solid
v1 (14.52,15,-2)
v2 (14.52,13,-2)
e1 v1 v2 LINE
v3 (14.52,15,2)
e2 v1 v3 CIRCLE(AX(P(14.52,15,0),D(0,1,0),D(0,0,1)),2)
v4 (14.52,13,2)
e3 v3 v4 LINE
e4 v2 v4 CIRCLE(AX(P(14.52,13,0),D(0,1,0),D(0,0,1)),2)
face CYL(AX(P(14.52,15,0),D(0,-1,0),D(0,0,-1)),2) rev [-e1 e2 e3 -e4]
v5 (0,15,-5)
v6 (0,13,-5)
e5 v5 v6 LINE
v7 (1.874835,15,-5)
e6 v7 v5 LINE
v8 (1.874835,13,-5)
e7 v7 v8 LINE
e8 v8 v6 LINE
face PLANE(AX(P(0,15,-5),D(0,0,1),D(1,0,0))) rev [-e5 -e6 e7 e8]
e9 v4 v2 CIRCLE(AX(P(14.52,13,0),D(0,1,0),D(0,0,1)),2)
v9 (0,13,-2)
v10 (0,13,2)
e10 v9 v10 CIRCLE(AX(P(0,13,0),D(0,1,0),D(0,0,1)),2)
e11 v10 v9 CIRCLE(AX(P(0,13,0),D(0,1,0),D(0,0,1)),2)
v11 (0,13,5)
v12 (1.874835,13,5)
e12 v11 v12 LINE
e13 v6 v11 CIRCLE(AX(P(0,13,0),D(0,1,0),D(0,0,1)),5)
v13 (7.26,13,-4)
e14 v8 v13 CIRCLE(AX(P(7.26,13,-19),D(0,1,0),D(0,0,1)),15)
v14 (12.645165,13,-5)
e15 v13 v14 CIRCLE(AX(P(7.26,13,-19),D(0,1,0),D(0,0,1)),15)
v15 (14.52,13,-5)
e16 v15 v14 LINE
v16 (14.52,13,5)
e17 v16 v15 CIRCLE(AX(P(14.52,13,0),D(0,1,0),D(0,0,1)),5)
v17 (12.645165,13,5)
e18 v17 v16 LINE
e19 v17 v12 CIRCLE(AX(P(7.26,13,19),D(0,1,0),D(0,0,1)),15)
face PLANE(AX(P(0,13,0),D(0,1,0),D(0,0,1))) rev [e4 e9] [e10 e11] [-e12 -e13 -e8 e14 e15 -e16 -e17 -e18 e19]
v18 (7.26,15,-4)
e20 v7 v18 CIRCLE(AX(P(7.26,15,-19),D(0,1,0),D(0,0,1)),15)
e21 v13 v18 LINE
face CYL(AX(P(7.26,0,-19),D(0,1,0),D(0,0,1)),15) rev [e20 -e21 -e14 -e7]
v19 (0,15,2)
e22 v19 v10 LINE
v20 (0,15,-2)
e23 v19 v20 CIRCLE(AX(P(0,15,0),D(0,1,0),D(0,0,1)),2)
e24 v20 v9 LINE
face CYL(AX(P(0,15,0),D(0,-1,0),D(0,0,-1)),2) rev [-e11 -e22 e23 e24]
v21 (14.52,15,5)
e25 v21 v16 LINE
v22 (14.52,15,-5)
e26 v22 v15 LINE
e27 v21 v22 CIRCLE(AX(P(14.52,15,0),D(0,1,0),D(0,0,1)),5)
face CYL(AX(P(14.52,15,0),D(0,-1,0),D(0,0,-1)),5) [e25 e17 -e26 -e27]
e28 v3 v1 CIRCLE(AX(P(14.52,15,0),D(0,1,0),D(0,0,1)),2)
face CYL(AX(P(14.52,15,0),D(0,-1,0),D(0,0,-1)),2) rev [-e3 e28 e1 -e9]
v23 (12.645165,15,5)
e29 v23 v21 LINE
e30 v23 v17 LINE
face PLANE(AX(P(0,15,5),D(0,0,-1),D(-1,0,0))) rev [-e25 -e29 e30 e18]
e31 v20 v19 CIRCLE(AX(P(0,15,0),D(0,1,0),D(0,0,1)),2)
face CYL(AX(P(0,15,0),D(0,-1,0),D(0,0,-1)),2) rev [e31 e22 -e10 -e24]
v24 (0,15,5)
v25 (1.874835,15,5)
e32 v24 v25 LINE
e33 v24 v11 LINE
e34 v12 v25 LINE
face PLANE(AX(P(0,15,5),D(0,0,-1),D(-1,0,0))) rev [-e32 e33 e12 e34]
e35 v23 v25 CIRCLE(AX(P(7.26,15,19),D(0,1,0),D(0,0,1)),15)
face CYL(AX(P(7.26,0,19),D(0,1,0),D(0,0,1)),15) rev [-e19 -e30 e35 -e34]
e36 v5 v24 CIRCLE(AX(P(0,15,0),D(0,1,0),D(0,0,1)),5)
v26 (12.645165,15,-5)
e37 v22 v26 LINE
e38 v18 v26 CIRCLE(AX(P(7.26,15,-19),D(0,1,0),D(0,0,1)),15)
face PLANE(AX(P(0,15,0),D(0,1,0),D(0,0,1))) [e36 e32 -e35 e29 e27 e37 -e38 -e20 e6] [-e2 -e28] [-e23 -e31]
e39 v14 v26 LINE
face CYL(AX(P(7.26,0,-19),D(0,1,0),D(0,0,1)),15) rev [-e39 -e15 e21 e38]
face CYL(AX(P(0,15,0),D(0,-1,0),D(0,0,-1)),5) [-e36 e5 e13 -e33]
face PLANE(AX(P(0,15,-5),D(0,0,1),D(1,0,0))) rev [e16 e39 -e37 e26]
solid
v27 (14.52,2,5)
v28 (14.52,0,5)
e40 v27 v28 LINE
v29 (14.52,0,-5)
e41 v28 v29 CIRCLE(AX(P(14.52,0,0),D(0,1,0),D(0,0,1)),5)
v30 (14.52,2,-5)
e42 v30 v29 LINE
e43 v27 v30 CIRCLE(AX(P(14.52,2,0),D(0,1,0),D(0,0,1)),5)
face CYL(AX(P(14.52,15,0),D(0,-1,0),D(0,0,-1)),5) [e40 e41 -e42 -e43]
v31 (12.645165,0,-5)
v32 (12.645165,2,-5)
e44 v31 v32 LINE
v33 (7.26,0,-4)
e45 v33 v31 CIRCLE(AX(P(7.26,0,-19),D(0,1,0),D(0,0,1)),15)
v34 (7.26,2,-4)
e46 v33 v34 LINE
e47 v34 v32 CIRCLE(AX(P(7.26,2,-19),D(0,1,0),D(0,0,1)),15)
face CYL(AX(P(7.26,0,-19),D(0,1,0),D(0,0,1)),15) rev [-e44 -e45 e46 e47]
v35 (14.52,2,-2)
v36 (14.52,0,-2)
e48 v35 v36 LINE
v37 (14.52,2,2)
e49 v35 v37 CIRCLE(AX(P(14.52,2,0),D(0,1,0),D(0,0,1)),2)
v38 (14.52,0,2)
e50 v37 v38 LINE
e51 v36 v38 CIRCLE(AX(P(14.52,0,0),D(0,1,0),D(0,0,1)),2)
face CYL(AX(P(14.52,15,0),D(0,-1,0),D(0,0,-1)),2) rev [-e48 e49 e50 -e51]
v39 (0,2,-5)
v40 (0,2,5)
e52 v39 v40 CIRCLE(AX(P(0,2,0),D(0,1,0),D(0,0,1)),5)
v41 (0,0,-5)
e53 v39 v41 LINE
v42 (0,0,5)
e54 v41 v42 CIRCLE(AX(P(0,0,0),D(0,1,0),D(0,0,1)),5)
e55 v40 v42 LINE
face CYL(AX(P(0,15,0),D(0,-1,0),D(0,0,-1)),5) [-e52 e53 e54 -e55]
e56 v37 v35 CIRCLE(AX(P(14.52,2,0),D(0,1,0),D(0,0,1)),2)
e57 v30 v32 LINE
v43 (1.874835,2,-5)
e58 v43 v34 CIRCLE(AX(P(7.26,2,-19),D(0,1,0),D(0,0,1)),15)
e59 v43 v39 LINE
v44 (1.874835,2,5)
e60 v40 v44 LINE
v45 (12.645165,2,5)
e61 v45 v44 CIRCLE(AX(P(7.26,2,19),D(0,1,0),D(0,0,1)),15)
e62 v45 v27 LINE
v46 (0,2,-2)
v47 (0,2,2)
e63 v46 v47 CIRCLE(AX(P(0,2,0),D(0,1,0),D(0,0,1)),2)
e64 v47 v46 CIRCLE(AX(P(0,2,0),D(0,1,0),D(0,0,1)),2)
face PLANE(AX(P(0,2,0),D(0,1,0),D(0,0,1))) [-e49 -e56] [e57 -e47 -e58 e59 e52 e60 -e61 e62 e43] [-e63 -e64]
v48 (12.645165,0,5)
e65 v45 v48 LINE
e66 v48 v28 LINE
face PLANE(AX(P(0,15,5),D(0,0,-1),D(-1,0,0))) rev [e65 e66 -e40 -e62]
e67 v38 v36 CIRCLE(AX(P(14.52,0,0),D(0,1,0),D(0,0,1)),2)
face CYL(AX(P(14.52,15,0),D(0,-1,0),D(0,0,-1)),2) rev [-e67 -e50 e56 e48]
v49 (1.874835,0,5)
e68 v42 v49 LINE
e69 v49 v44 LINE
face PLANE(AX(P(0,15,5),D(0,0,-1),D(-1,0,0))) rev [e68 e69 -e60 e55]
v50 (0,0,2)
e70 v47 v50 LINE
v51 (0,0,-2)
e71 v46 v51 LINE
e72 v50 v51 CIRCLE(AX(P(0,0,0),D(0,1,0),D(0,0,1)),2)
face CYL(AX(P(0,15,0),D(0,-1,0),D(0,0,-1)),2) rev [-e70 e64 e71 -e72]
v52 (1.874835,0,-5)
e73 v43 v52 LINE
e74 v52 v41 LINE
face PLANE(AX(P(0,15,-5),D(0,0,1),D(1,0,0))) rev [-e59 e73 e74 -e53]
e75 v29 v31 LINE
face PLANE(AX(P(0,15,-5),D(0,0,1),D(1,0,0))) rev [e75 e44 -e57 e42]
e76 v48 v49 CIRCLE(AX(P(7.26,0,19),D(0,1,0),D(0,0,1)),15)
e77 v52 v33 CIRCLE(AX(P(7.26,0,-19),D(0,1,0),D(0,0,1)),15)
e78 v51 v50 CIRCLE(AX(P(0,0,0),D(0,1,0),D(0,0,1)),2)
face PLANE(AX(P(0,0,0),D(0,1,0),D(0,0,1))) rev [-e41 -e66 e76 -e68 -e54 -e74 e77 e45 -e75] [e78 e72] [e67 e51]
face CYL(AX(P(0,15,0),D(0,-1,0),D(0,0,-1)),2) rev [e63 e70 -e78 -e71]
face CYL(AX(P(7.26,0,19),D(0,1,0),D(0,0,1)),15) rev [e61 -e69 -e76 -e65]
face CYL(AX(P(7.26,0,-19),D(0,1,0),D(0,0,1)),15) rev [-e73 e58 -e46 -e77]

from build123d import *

# Parameters (mm, degrees)
SKETCH1_R               = 2
BOSS_EXTRUDE1_DEPTH     = 15
CUT_EXTRUDE1_DEPTH      = 5.5
CUT_EXTRUDE1_DEPTH_BACK = 5.5
SKETCH4_R               = 15
CUT_EXTRUDE2_DEPTH      = 15


with BuildPart() as part:
    # Sketch1 → Boss-Extrude1 (new body)
    with BuildSketch(Plane(origin=(0, 0, 0), x_dir=(1, 0, 0), z_dir=(0, 1, 0))):
        with BuildLine():
            Line((0, 5), (14.52, 5))
            ThreePointArc((14.52, 5), (19.52, 0), (14.52, -5))
            Line((14.52, -5), (0, -5))
            ThreePointArc((0, -5), (-5, 0), (0, 5))
        make_face()
        with Locations(Location((0, 0, 0), (0, 0, 270))):
            Circle(SKETCH1_R, mode=Mode.SUBTRACT)
        with Locations(Location((14.52, 0, 0), (0, 0, 270))):
            Circle(SKETCH1_R, mode=Mode.SUBTRACT)
    extrude(amount=BOSS_EXTRUDE1_DEPTH)

    # Sketch2 → Cut-Extrude1 (cut, two sides: drawn at the far end of the back side and taken through both)
    with BuildSketch(Plane(origin=(0, 7.5, 0), x_dir=(1, 0, 0), z_dir=(0, 1, 0)).offset(-CUT_EXTRUDE1_DEPTH_BACK)):
        with BuildLine():
            Line((0, 6.90174959), (14.52, 6.90174959))
            ThreePointArc((14.52, 6.90174959), (21.42174959, 0), (14.52, -6.90174959))
            Line((14.52, -6.90174959), (0, -6.90174959))
            ThreePointArc((0, -6.90174959), (-6.90174959, 0), (0, 6.90174959))
        make_face()
    extrude(amount=CUT_EXTRUDE1_DEPTH + CUT_EXTRUDE1_DEPTH_BACK, mode=Mode.SUBTRACT)


with BuildPart() as cut_extrude1_piece_1:
    # of the separate pieces the step leaves, piece 1, a body of its own (cut_extrude1_pieces)
    add(part.part.solids().sort_by_distance((14.52, 0, 5))[0])


with BuildPart() as cut_extrude1_piece_2:
    # of the separate pieces the step leaves, piece 2, a body of its own (cut_extrude1_pieces)
    add(part.part.solids().sort_by_distance((0, 13, 5))[0])


with BuildPart() as cut_extrude2_tool:
    # Sketch4 → Cut-Extrude2 (new body)
    with BuildSketch(Plane(origin=(0, 15, 0), x_dir=(1, 0, 0), z_dir=(0, 1, 0))):
        with Locations((7.26, 19)):
            Circle(SKETCH4_R)
        with Locations((7.26, -19)):
            Circle(SKETCH4_R)
    extrude(amount=-CUT_EXTRUDE2_DEPTH)


with BuildPart() as cut_extrude1_piece_1_1:
    add(cut_extrude1_piece_1.part)

    # Cut-Extrude2: cut by cut_extrude2_tool
    add(cut_extrude2_tool.part, mode=Mode.SUBTRACT)


with BuildPart() as cut_extrude1_piece_2_1:
    add(cut_extrude1_piece_2.part)

    # Cut-Extrude2: cut by cut_extrude2_tool
    add(cut_extrude2_tool.part, mode=Mode.SUBTRACT)


solid = Compound([cut_extrude1_piece_1_1.part, cut_extrude1_piece_2_1.part])
